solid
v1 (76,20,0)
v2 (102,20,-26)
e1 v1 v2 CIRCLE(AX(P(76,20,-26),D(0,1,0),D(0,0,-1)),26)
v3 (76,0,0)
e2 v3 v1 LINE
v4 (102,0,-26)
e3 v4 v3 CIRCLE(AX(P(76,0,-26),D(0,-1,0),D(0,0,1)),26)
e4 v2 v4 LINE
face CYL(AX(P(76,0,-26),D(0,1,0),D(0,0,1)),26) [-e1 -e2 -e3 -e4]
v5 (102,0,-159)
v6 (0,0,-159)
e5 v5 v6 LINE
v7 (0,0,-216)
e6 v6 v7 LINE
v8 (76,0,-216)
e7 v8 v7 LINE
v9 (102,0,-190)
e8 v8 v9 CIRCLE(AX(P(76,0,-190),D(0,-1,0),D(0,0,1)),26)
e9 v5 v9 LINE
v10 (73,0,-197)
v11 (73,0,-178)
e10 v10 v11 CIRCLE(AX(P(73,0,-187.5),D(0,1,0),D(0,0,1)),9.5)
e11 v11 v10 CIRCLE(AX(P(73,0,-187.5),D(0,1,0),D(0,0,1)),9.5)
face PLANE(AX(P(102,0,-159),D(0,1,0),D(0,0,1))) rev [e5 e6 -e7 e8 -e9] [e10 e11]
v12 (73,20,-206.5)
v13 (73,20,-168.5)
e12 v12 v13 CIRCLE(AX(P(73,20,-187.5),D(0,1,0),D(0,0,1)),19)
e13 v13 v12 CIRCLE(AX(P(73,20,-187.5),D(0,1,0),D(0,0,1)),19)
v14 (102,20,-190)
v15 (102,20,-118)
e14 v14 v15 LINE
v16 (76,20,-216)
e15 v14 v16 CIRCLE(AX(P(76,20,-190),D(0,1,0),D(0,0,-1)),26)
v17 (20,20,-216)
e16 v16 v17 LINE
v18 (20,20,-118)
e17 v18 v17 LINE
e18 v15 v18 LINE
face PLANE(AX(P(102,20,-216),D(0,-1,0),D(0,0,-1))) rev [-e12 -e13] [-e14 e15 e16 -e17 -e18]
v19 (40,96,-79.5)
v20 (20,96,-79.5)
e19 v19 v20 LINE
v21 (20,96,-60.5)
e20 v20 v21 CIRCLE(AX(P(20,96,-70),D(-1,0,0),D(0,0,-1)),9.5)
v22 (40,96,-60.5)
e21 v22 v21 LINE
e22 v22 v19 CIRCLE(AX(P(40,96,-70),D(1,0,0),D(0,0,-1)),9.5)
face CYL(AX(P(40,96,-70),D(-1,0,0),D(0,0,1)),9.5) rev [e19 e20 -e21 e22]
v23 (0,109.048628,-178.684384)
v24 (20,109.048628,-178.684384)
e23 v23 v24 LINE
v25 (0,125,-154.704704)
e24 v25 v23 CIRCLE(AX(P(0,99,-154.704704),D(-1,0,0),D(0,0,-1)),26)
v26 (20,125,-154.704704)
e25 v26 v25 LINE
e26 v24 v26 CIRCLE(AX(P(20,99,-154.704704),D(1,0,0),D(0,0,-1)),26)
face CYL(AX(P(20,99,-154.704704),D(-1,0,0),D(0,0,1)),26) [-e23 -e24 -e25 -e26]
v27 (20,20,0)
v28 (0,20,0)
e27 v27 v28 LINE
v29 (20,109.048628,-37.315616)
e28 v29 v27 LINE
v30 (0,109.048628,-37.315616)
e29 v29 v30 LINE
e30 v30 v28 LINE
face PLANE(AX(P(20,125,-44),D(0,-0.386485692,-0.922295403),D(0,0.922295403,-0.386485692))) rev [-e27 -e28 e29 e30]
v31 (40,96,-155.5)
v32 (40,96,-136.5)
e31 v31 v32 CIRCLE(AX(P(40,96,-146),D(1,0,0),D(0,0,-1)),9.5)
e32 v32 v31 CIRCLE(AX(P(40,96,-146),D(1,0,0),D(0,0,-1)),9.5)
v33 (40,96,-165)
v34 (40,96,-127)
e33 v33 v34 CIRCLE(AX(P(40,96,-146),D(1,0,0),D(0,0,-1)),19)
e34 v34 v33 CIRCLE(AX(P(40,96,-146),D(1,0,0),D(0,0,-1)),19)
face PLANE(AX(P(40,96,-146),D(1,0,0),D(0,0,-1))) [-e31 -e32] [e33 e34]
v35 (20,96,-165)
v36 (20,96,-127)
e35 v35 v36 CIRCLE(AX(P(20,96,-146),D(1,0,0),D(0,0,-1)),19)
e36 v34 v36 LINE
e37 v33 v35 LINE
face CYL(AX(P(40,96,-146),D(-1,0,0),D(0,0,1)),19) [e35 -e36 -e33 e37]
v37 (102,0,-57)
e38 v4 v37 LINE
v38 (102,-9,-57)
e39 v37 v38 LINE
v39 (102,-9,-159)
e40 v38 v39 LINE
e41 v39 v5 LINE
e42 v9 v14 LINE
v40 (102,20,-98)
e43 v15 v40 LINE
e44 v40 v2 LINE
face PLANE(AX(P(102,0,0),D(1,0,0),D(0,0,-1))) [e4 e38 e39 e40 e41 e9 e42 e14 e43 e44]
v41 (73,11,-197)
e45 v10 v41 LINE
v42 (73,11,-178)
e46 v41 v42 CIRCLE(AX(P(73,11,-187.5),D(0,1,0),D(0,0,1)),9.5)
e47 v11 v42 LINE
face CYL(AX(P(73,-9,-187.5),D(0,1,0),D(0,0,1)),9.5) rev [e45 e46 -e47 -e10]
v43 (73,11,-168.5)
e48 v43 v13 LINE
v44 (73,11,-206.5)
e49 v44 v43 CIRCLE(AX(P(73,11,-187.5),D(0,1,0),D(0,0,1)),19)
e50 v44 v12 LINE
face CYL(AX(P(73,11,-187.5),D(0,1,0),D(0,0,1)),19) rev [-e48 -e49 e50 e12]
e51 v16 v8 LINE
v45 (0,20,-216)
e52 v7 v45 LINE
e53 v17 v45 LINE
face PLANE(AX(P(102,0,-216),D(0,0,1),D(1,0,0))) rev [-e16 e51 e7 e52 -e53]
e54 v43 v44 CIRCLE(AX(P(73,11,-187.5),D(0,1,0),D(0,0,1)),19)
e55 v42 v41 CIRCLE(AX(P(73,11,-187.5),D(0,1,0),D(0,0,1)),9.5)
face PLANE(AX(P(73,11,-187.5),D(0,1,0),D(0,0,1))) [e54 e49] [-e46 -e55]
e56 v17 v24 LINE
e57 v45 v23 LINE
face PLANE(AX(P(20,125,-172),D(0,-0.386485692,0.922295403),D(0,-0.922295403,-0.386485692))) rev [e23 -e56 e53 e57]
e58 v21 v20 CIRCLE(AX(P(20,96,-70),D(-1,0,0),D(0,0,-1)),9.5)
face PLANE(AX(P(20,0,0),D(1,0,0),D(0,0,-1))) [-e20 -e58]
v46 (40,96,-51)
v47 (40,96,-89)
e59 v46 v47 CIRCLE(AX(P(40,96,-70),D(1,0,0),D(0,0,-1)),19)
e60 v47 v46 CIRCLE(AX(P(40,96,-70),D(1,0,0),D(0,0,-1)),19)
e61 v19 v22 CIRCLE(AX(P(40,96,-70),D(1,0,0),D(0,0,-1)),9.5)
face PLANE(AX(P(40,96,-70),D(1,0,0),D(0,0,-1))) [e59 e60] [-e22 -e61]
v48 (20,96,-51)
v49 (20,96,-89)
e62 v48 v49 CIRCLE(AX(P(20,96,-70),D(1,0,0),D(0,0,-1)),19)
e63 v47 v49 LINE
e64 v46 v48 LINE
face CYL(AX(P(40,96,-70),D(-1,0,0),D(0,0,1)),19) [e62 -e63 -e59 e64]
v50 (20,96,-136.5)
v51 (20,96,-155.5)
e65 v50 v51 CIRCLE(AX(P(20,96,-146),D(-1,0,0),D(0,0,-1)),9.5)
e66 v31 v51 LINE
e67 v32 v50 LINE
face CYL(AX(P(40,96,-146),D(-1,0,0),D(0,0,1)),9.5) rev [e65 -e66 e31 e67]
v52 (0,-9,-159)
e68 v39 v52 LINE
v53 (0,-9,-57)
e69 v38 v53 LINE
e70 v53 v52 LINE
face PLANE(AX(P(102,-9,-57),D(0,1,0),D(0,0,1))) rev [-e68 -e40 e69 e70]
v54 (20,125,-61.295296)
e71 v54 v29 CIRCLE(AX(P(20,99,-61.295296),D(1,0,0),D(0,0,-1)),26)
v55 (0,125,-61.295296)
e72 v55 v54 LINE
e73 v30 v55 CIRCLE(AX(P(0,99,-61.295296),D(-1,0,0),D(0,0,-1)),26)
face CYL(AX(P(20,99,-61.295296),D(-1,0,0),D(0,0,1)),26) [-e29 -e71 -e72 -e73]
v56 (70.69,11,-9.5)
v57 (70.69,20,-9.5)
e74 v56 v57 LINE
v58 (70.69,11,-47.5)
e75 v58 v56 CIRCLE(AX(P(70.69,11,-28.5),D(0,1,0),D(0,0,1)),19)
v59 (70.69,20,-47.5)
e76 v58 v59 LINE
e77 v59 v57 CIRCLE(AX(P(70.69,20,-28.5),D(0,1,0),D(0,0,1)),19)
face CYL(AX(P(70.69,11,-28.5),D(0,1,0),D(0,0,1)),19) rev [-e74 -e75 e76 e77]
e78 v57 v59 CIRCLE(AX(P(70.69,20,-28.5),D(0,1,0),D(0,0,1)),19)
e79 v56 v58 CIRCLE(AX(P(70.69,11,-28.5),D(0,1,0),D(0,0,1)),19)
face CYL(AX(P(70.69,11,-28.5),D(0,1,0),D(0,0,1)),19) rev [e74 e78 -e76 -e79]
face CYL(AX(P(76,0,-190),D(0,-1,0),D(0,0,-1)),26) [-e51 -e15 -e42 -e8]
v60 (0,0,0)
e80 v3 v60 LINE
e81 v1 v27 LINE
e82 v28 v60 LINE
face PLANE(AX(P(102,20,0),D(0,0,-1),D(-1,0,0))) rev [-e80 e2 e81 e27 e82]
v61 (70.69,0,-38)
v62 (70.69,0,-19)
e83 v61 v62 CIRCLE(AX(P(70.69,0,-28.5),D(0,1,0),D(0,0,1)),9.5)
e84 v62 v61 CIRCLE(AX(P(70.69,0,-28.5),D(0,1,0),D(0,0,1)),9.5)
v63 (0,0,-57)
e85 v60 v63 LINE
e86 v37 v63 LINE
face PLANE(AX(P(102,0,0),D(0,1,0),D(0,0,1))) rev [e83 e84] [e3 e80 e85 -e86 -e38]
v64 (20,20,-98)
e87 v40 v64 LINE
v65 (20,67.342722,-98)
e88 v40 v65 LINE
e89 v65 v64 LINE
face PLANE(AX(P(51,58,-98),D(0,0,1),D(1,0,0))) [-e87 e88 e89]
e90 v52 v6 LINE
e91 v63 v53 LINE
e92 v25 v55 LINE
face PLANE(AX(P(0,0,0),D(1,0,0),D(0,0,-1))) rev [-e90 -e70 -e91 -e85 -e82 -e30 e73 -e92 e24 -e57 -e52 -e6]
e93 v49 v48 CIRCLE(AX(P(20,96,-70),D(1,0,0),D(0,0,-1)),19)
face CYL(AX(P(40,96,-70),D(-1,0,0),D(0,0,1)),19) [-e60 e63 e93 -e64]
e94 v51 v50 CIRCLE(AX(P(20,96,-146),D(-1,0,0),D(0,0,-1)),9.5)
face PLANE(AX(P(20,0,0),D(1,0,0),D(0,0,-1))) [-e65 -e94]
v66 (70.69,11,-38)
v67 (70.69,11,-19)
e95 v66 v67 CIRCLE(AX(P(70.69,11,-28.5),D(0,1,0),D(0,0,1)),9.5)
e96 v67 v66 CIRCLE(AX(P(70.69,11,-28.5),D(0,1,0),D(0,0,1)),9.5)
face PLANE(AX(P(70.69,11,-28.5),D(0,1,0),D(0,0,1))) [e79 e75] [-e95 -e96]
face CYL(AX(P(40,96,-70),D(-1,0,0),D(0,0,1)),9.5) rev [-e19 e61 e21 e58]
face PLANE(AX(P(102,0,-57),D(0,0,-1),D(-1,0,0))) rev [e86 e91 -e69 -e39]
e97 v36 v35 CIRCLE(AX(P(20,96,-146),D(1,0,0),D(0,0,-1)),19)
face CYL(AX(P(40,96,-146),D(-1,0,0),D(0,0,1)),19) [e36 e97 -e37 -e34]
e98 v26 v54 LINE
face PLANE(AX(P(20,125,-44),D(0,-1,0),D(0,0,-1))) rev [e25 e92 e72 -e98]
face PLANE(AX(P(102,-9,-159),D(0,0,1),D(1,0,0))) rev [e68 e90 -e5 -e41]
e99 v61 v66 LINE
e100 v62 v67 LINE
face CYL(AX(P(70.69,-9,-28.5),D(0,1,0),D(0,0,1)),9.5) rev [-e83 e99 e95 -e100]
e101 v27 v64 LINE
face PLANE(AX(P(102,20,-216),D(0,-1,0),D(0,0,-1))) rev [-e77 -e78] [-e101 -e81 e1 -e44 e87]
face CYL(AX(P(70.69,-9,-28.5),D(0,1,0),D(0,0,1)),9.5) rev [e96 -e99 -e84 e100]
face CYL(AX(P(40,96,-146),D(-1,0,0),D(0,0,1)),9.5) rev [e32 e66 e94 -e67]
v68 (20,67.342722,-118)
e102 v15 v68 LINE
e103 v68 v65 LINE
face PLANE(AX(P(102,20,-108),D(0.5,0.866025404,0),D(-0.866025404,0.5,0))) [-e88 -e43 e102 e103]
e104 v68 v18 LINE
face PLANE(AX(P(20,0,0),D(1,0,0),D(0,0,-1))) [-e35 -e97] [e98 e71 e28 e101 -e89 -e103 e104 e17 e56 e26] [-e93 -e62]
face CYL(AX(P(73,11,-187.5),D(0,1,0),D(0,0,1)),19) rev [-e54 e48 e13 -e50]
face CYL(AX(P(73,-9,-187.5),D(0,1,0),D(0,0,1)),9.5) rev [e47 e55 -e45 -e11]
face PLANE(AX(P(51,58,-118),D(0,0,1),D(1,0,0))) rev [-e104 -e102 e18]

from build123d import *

# Parameters (mm, degrees)
BASE_PLATE_DEPTH                = 102
UPRIGHT_PLATE_DEPTH             = 20
UPRIGHT_BOSS_1_PROFILE_R        = 19
UPRIGHT_BOSS_1_PROFILE_R_2      = 9.5
UPRIGHT_BOSS_1_DEPTH            = 20
UPRIGHT_BOSS_2_PROFILE_R        = 19
UPRIGHT_BOSS_2_PROFILE_R_2      = 9.5
UPRIGHT_BOSS_2_DEPTH            = 20
BASE_POCKET_1_PROFILE_R         = 19
BASE_POCKET_1_DEPTH             = 9
MOUNTING_HOLE_1_PROFILE_R       = 9.5
MOUNTING_HOLE_1_DEPTH           = 265.680940001
BASE_POCKET_2_PROFILE_R         = 19
BASE_POCKET_2_DEPTH             = 9
MOUNTING_HOLE_2_PROFILE_R       = 9.5
MOUNTING_HOLE_2_DEPTH           = 265.680940001
UPRIGHT_CORNER_FILLET_R26_1_R   = 26
UPRIGHT_CORNER_FILLET_R26_2_R   = 26
BASE_CORNER_FILLETS_R26_R       = 26
GUSSET_RIB_REACH                = 196.147
GUSSET_RIB_PROFILE_30DEG_WALL_W = 484.979147418
GUSSET_RIB_PROFILE_30DEG_WALL_H = 20


with BuildPart() as part:
    # Base Plate Profile → Base Plate (new body)
    with BuildSketch(Plane(origin=(0, 0, 0), x_dir=(0, 0, -1), z_dir=(1, 0, 0))):
        Polygon((0, 0), (57, 0), (57, -9), (159, -9), (159, 0), (216, 0), (216, 20), (0, 20), align=None)
    extrude(amount=BASE_PLATE_DEPTH)

    # Upright Plate Profile → Upright Plate (add)
    with BuildSketch(Plane(origin=(0, 0, 0), x_dir=(0, 0, -1), z_dir=(1, 0, 0))):
        Polygon((0, 20), (216, 20), (172, 125), (44, 125), align=None)
    extrude(amount=UPRIGHT_PLATE_DEPTH)

    # Upright Boss 1 Profile → Upright Boss 1 (add)
    with BuildSketch(Plane(origin=(20, 0, 0), x_dir=(0, 0, -1), z_dir=(1, 0, 0))):
        with Locations((70, 96)):
            Circle(UPRIGHT_BOSS_1_PROFILE_R)
        with Locations((70, 96)):
            Circle(UPRIGHT_BOSS_1_PROFILE_R_2, mode=Mode.SUBTRACT)
    extrude(amount=UPRIGHT_BOSS_1_DEPTH)

    # Upright Boss 2 Profile → Upright Boss 2 (add)
    with BuildSketch(Plane(origin=(20, 0, 0), x_dir=(0, 0, -1), z_dir=(1, 0, 0))):
        with Locations((146, 96)):
            Circle(UPRIGHT_BOSS_2_PROFILE_R)
        with Locations((146, 96)):
            Circle(UPRIGHT_BOSS_2_PROFILE_R_2, mode=Mode.SUBTRACT)
    extrude(amount=UPRIGHT_BOSS_2_DEPTH)

    # Base Pocket 1 Profile → Base Pocket 1 (cut)
    with BuildSketch(Plane(origin=(0, 20, 0), x_dir=(1, 0, 0), z_dir=(0, 1, 0))):
        with Locations(Location((73, 187.5, 0), (0, 0, 270))):
            Circle(BASE_POCKET_1_PROFILE_R)
    extrude(amount=-BASE_POCKET_1_DEPTH, mode=Mode.SUBTRACT)

    # Mounting Hole 1 Profile → Mounting Hole 1 (cut, through all)
    with BuildSketch(Plane(origin=(0, 11, 0), x_dir=(1, 0, 0), z_dir=(0, 1, 0))):
        with Locations(Location((73, 187.5, 0), (0, 0, 270))):
            Circle(MOUNTING_HOLE_1_PROFILE_R)
    extrude(amount=-MOUNTING_HOLE_1_DEPTH, mode=Mode.SUBTRACT)

    # Base Pocket 2 Profile → Base Pocket 2 (cut)
    with BuildSketch(Plane(origin=(0, 20, 0), x_dir=(1, 0, 0), z_dir=(0, 1, 0))):
        with Locations(Location((70.69, 28.5, 0), (0, 0, 270))):
            Circle(BASE_POCKET_2_PROFILE_R)
    extrude(amount=-BASE_POCKET_2_DEPTH, mode=Mode.SUBTRACT)

    # Mounting Hole 2 Profile → Mounting Hole 2 (cut, through all)
    with BuildSketch(Plane(origin=(0, 11, 0), x_dir=(1, 0, 0), z_dir=(0, 1, 0))):
        with Locations(Location((70.69, 28.5, 0), (0, 0, 270))):
            Circle(MOUNTING_HOLE_2_PROFILE_R)
    extrude(amount=-MOUNTING_HOLE_2_DEPTH, mode=Mode.SUBTRACT)

    # Upright Corner Fillet R26 1
    upright_corner_fillet_r26_1_edges = [part.edges().sort_by_distance(p)[0] for p in [
        (10, 125, -44),
    ]]
    fillet(upright_corner_fillet_r26_1_edges, radius=UPRIGHT_CORNER_FILLET_R26_1_R)

    # Upright Corner Fillet R26 2
    upright_corner_fillet_r26_2_edges = [part.edges().sort_by_distance(p)[0] for p in [
        (10, 125, -172),
    ]]
    fillet(upright_corner_fillet_r26_2_edges, radius=UPRIGHT_CORNER_FILLET_R26_2_R)

    # Base Corner Fillets R26
    base_corner_fillets_r26_edges = [part.edges().sort_by_distance(p)[0] for p in [
        (102, 10, -216),
        (102, 10, 0),
    ]]
    fillet(base_corner_fillets_r26_edges, radius=BASE_CORNER_FILLETS_R26_R)

    # Gusset Rib Profile 30deg wall → Gusset Rib (add, up to next)
    with BuildSketch(Plane(origin=(61, 43.671361037, -108), x_dir=(-0.866025403782, 0.500000000004, 0), z_dir=(-0.500000000004, -0.866025403782, 0)), mode=Mode.PRIVATE) as gusset_rib_sk1:
        Rectangle(GUSSET_RIB_PROFILE_30DEG_WALL_W, GUSSET_RIB_PROFILE_30DEG_WALL_H)
    gusset_rib_tool1 = extrude(gusset_rib_sk1.sketch, amount=GUSSET_RIB_REACH, mode=Mode.PRIVATE) - part.part
    add(gusset_rib_tool1.solids().sort_by_distance((61, 43.671361037, -108))[0])


solid = part.part
